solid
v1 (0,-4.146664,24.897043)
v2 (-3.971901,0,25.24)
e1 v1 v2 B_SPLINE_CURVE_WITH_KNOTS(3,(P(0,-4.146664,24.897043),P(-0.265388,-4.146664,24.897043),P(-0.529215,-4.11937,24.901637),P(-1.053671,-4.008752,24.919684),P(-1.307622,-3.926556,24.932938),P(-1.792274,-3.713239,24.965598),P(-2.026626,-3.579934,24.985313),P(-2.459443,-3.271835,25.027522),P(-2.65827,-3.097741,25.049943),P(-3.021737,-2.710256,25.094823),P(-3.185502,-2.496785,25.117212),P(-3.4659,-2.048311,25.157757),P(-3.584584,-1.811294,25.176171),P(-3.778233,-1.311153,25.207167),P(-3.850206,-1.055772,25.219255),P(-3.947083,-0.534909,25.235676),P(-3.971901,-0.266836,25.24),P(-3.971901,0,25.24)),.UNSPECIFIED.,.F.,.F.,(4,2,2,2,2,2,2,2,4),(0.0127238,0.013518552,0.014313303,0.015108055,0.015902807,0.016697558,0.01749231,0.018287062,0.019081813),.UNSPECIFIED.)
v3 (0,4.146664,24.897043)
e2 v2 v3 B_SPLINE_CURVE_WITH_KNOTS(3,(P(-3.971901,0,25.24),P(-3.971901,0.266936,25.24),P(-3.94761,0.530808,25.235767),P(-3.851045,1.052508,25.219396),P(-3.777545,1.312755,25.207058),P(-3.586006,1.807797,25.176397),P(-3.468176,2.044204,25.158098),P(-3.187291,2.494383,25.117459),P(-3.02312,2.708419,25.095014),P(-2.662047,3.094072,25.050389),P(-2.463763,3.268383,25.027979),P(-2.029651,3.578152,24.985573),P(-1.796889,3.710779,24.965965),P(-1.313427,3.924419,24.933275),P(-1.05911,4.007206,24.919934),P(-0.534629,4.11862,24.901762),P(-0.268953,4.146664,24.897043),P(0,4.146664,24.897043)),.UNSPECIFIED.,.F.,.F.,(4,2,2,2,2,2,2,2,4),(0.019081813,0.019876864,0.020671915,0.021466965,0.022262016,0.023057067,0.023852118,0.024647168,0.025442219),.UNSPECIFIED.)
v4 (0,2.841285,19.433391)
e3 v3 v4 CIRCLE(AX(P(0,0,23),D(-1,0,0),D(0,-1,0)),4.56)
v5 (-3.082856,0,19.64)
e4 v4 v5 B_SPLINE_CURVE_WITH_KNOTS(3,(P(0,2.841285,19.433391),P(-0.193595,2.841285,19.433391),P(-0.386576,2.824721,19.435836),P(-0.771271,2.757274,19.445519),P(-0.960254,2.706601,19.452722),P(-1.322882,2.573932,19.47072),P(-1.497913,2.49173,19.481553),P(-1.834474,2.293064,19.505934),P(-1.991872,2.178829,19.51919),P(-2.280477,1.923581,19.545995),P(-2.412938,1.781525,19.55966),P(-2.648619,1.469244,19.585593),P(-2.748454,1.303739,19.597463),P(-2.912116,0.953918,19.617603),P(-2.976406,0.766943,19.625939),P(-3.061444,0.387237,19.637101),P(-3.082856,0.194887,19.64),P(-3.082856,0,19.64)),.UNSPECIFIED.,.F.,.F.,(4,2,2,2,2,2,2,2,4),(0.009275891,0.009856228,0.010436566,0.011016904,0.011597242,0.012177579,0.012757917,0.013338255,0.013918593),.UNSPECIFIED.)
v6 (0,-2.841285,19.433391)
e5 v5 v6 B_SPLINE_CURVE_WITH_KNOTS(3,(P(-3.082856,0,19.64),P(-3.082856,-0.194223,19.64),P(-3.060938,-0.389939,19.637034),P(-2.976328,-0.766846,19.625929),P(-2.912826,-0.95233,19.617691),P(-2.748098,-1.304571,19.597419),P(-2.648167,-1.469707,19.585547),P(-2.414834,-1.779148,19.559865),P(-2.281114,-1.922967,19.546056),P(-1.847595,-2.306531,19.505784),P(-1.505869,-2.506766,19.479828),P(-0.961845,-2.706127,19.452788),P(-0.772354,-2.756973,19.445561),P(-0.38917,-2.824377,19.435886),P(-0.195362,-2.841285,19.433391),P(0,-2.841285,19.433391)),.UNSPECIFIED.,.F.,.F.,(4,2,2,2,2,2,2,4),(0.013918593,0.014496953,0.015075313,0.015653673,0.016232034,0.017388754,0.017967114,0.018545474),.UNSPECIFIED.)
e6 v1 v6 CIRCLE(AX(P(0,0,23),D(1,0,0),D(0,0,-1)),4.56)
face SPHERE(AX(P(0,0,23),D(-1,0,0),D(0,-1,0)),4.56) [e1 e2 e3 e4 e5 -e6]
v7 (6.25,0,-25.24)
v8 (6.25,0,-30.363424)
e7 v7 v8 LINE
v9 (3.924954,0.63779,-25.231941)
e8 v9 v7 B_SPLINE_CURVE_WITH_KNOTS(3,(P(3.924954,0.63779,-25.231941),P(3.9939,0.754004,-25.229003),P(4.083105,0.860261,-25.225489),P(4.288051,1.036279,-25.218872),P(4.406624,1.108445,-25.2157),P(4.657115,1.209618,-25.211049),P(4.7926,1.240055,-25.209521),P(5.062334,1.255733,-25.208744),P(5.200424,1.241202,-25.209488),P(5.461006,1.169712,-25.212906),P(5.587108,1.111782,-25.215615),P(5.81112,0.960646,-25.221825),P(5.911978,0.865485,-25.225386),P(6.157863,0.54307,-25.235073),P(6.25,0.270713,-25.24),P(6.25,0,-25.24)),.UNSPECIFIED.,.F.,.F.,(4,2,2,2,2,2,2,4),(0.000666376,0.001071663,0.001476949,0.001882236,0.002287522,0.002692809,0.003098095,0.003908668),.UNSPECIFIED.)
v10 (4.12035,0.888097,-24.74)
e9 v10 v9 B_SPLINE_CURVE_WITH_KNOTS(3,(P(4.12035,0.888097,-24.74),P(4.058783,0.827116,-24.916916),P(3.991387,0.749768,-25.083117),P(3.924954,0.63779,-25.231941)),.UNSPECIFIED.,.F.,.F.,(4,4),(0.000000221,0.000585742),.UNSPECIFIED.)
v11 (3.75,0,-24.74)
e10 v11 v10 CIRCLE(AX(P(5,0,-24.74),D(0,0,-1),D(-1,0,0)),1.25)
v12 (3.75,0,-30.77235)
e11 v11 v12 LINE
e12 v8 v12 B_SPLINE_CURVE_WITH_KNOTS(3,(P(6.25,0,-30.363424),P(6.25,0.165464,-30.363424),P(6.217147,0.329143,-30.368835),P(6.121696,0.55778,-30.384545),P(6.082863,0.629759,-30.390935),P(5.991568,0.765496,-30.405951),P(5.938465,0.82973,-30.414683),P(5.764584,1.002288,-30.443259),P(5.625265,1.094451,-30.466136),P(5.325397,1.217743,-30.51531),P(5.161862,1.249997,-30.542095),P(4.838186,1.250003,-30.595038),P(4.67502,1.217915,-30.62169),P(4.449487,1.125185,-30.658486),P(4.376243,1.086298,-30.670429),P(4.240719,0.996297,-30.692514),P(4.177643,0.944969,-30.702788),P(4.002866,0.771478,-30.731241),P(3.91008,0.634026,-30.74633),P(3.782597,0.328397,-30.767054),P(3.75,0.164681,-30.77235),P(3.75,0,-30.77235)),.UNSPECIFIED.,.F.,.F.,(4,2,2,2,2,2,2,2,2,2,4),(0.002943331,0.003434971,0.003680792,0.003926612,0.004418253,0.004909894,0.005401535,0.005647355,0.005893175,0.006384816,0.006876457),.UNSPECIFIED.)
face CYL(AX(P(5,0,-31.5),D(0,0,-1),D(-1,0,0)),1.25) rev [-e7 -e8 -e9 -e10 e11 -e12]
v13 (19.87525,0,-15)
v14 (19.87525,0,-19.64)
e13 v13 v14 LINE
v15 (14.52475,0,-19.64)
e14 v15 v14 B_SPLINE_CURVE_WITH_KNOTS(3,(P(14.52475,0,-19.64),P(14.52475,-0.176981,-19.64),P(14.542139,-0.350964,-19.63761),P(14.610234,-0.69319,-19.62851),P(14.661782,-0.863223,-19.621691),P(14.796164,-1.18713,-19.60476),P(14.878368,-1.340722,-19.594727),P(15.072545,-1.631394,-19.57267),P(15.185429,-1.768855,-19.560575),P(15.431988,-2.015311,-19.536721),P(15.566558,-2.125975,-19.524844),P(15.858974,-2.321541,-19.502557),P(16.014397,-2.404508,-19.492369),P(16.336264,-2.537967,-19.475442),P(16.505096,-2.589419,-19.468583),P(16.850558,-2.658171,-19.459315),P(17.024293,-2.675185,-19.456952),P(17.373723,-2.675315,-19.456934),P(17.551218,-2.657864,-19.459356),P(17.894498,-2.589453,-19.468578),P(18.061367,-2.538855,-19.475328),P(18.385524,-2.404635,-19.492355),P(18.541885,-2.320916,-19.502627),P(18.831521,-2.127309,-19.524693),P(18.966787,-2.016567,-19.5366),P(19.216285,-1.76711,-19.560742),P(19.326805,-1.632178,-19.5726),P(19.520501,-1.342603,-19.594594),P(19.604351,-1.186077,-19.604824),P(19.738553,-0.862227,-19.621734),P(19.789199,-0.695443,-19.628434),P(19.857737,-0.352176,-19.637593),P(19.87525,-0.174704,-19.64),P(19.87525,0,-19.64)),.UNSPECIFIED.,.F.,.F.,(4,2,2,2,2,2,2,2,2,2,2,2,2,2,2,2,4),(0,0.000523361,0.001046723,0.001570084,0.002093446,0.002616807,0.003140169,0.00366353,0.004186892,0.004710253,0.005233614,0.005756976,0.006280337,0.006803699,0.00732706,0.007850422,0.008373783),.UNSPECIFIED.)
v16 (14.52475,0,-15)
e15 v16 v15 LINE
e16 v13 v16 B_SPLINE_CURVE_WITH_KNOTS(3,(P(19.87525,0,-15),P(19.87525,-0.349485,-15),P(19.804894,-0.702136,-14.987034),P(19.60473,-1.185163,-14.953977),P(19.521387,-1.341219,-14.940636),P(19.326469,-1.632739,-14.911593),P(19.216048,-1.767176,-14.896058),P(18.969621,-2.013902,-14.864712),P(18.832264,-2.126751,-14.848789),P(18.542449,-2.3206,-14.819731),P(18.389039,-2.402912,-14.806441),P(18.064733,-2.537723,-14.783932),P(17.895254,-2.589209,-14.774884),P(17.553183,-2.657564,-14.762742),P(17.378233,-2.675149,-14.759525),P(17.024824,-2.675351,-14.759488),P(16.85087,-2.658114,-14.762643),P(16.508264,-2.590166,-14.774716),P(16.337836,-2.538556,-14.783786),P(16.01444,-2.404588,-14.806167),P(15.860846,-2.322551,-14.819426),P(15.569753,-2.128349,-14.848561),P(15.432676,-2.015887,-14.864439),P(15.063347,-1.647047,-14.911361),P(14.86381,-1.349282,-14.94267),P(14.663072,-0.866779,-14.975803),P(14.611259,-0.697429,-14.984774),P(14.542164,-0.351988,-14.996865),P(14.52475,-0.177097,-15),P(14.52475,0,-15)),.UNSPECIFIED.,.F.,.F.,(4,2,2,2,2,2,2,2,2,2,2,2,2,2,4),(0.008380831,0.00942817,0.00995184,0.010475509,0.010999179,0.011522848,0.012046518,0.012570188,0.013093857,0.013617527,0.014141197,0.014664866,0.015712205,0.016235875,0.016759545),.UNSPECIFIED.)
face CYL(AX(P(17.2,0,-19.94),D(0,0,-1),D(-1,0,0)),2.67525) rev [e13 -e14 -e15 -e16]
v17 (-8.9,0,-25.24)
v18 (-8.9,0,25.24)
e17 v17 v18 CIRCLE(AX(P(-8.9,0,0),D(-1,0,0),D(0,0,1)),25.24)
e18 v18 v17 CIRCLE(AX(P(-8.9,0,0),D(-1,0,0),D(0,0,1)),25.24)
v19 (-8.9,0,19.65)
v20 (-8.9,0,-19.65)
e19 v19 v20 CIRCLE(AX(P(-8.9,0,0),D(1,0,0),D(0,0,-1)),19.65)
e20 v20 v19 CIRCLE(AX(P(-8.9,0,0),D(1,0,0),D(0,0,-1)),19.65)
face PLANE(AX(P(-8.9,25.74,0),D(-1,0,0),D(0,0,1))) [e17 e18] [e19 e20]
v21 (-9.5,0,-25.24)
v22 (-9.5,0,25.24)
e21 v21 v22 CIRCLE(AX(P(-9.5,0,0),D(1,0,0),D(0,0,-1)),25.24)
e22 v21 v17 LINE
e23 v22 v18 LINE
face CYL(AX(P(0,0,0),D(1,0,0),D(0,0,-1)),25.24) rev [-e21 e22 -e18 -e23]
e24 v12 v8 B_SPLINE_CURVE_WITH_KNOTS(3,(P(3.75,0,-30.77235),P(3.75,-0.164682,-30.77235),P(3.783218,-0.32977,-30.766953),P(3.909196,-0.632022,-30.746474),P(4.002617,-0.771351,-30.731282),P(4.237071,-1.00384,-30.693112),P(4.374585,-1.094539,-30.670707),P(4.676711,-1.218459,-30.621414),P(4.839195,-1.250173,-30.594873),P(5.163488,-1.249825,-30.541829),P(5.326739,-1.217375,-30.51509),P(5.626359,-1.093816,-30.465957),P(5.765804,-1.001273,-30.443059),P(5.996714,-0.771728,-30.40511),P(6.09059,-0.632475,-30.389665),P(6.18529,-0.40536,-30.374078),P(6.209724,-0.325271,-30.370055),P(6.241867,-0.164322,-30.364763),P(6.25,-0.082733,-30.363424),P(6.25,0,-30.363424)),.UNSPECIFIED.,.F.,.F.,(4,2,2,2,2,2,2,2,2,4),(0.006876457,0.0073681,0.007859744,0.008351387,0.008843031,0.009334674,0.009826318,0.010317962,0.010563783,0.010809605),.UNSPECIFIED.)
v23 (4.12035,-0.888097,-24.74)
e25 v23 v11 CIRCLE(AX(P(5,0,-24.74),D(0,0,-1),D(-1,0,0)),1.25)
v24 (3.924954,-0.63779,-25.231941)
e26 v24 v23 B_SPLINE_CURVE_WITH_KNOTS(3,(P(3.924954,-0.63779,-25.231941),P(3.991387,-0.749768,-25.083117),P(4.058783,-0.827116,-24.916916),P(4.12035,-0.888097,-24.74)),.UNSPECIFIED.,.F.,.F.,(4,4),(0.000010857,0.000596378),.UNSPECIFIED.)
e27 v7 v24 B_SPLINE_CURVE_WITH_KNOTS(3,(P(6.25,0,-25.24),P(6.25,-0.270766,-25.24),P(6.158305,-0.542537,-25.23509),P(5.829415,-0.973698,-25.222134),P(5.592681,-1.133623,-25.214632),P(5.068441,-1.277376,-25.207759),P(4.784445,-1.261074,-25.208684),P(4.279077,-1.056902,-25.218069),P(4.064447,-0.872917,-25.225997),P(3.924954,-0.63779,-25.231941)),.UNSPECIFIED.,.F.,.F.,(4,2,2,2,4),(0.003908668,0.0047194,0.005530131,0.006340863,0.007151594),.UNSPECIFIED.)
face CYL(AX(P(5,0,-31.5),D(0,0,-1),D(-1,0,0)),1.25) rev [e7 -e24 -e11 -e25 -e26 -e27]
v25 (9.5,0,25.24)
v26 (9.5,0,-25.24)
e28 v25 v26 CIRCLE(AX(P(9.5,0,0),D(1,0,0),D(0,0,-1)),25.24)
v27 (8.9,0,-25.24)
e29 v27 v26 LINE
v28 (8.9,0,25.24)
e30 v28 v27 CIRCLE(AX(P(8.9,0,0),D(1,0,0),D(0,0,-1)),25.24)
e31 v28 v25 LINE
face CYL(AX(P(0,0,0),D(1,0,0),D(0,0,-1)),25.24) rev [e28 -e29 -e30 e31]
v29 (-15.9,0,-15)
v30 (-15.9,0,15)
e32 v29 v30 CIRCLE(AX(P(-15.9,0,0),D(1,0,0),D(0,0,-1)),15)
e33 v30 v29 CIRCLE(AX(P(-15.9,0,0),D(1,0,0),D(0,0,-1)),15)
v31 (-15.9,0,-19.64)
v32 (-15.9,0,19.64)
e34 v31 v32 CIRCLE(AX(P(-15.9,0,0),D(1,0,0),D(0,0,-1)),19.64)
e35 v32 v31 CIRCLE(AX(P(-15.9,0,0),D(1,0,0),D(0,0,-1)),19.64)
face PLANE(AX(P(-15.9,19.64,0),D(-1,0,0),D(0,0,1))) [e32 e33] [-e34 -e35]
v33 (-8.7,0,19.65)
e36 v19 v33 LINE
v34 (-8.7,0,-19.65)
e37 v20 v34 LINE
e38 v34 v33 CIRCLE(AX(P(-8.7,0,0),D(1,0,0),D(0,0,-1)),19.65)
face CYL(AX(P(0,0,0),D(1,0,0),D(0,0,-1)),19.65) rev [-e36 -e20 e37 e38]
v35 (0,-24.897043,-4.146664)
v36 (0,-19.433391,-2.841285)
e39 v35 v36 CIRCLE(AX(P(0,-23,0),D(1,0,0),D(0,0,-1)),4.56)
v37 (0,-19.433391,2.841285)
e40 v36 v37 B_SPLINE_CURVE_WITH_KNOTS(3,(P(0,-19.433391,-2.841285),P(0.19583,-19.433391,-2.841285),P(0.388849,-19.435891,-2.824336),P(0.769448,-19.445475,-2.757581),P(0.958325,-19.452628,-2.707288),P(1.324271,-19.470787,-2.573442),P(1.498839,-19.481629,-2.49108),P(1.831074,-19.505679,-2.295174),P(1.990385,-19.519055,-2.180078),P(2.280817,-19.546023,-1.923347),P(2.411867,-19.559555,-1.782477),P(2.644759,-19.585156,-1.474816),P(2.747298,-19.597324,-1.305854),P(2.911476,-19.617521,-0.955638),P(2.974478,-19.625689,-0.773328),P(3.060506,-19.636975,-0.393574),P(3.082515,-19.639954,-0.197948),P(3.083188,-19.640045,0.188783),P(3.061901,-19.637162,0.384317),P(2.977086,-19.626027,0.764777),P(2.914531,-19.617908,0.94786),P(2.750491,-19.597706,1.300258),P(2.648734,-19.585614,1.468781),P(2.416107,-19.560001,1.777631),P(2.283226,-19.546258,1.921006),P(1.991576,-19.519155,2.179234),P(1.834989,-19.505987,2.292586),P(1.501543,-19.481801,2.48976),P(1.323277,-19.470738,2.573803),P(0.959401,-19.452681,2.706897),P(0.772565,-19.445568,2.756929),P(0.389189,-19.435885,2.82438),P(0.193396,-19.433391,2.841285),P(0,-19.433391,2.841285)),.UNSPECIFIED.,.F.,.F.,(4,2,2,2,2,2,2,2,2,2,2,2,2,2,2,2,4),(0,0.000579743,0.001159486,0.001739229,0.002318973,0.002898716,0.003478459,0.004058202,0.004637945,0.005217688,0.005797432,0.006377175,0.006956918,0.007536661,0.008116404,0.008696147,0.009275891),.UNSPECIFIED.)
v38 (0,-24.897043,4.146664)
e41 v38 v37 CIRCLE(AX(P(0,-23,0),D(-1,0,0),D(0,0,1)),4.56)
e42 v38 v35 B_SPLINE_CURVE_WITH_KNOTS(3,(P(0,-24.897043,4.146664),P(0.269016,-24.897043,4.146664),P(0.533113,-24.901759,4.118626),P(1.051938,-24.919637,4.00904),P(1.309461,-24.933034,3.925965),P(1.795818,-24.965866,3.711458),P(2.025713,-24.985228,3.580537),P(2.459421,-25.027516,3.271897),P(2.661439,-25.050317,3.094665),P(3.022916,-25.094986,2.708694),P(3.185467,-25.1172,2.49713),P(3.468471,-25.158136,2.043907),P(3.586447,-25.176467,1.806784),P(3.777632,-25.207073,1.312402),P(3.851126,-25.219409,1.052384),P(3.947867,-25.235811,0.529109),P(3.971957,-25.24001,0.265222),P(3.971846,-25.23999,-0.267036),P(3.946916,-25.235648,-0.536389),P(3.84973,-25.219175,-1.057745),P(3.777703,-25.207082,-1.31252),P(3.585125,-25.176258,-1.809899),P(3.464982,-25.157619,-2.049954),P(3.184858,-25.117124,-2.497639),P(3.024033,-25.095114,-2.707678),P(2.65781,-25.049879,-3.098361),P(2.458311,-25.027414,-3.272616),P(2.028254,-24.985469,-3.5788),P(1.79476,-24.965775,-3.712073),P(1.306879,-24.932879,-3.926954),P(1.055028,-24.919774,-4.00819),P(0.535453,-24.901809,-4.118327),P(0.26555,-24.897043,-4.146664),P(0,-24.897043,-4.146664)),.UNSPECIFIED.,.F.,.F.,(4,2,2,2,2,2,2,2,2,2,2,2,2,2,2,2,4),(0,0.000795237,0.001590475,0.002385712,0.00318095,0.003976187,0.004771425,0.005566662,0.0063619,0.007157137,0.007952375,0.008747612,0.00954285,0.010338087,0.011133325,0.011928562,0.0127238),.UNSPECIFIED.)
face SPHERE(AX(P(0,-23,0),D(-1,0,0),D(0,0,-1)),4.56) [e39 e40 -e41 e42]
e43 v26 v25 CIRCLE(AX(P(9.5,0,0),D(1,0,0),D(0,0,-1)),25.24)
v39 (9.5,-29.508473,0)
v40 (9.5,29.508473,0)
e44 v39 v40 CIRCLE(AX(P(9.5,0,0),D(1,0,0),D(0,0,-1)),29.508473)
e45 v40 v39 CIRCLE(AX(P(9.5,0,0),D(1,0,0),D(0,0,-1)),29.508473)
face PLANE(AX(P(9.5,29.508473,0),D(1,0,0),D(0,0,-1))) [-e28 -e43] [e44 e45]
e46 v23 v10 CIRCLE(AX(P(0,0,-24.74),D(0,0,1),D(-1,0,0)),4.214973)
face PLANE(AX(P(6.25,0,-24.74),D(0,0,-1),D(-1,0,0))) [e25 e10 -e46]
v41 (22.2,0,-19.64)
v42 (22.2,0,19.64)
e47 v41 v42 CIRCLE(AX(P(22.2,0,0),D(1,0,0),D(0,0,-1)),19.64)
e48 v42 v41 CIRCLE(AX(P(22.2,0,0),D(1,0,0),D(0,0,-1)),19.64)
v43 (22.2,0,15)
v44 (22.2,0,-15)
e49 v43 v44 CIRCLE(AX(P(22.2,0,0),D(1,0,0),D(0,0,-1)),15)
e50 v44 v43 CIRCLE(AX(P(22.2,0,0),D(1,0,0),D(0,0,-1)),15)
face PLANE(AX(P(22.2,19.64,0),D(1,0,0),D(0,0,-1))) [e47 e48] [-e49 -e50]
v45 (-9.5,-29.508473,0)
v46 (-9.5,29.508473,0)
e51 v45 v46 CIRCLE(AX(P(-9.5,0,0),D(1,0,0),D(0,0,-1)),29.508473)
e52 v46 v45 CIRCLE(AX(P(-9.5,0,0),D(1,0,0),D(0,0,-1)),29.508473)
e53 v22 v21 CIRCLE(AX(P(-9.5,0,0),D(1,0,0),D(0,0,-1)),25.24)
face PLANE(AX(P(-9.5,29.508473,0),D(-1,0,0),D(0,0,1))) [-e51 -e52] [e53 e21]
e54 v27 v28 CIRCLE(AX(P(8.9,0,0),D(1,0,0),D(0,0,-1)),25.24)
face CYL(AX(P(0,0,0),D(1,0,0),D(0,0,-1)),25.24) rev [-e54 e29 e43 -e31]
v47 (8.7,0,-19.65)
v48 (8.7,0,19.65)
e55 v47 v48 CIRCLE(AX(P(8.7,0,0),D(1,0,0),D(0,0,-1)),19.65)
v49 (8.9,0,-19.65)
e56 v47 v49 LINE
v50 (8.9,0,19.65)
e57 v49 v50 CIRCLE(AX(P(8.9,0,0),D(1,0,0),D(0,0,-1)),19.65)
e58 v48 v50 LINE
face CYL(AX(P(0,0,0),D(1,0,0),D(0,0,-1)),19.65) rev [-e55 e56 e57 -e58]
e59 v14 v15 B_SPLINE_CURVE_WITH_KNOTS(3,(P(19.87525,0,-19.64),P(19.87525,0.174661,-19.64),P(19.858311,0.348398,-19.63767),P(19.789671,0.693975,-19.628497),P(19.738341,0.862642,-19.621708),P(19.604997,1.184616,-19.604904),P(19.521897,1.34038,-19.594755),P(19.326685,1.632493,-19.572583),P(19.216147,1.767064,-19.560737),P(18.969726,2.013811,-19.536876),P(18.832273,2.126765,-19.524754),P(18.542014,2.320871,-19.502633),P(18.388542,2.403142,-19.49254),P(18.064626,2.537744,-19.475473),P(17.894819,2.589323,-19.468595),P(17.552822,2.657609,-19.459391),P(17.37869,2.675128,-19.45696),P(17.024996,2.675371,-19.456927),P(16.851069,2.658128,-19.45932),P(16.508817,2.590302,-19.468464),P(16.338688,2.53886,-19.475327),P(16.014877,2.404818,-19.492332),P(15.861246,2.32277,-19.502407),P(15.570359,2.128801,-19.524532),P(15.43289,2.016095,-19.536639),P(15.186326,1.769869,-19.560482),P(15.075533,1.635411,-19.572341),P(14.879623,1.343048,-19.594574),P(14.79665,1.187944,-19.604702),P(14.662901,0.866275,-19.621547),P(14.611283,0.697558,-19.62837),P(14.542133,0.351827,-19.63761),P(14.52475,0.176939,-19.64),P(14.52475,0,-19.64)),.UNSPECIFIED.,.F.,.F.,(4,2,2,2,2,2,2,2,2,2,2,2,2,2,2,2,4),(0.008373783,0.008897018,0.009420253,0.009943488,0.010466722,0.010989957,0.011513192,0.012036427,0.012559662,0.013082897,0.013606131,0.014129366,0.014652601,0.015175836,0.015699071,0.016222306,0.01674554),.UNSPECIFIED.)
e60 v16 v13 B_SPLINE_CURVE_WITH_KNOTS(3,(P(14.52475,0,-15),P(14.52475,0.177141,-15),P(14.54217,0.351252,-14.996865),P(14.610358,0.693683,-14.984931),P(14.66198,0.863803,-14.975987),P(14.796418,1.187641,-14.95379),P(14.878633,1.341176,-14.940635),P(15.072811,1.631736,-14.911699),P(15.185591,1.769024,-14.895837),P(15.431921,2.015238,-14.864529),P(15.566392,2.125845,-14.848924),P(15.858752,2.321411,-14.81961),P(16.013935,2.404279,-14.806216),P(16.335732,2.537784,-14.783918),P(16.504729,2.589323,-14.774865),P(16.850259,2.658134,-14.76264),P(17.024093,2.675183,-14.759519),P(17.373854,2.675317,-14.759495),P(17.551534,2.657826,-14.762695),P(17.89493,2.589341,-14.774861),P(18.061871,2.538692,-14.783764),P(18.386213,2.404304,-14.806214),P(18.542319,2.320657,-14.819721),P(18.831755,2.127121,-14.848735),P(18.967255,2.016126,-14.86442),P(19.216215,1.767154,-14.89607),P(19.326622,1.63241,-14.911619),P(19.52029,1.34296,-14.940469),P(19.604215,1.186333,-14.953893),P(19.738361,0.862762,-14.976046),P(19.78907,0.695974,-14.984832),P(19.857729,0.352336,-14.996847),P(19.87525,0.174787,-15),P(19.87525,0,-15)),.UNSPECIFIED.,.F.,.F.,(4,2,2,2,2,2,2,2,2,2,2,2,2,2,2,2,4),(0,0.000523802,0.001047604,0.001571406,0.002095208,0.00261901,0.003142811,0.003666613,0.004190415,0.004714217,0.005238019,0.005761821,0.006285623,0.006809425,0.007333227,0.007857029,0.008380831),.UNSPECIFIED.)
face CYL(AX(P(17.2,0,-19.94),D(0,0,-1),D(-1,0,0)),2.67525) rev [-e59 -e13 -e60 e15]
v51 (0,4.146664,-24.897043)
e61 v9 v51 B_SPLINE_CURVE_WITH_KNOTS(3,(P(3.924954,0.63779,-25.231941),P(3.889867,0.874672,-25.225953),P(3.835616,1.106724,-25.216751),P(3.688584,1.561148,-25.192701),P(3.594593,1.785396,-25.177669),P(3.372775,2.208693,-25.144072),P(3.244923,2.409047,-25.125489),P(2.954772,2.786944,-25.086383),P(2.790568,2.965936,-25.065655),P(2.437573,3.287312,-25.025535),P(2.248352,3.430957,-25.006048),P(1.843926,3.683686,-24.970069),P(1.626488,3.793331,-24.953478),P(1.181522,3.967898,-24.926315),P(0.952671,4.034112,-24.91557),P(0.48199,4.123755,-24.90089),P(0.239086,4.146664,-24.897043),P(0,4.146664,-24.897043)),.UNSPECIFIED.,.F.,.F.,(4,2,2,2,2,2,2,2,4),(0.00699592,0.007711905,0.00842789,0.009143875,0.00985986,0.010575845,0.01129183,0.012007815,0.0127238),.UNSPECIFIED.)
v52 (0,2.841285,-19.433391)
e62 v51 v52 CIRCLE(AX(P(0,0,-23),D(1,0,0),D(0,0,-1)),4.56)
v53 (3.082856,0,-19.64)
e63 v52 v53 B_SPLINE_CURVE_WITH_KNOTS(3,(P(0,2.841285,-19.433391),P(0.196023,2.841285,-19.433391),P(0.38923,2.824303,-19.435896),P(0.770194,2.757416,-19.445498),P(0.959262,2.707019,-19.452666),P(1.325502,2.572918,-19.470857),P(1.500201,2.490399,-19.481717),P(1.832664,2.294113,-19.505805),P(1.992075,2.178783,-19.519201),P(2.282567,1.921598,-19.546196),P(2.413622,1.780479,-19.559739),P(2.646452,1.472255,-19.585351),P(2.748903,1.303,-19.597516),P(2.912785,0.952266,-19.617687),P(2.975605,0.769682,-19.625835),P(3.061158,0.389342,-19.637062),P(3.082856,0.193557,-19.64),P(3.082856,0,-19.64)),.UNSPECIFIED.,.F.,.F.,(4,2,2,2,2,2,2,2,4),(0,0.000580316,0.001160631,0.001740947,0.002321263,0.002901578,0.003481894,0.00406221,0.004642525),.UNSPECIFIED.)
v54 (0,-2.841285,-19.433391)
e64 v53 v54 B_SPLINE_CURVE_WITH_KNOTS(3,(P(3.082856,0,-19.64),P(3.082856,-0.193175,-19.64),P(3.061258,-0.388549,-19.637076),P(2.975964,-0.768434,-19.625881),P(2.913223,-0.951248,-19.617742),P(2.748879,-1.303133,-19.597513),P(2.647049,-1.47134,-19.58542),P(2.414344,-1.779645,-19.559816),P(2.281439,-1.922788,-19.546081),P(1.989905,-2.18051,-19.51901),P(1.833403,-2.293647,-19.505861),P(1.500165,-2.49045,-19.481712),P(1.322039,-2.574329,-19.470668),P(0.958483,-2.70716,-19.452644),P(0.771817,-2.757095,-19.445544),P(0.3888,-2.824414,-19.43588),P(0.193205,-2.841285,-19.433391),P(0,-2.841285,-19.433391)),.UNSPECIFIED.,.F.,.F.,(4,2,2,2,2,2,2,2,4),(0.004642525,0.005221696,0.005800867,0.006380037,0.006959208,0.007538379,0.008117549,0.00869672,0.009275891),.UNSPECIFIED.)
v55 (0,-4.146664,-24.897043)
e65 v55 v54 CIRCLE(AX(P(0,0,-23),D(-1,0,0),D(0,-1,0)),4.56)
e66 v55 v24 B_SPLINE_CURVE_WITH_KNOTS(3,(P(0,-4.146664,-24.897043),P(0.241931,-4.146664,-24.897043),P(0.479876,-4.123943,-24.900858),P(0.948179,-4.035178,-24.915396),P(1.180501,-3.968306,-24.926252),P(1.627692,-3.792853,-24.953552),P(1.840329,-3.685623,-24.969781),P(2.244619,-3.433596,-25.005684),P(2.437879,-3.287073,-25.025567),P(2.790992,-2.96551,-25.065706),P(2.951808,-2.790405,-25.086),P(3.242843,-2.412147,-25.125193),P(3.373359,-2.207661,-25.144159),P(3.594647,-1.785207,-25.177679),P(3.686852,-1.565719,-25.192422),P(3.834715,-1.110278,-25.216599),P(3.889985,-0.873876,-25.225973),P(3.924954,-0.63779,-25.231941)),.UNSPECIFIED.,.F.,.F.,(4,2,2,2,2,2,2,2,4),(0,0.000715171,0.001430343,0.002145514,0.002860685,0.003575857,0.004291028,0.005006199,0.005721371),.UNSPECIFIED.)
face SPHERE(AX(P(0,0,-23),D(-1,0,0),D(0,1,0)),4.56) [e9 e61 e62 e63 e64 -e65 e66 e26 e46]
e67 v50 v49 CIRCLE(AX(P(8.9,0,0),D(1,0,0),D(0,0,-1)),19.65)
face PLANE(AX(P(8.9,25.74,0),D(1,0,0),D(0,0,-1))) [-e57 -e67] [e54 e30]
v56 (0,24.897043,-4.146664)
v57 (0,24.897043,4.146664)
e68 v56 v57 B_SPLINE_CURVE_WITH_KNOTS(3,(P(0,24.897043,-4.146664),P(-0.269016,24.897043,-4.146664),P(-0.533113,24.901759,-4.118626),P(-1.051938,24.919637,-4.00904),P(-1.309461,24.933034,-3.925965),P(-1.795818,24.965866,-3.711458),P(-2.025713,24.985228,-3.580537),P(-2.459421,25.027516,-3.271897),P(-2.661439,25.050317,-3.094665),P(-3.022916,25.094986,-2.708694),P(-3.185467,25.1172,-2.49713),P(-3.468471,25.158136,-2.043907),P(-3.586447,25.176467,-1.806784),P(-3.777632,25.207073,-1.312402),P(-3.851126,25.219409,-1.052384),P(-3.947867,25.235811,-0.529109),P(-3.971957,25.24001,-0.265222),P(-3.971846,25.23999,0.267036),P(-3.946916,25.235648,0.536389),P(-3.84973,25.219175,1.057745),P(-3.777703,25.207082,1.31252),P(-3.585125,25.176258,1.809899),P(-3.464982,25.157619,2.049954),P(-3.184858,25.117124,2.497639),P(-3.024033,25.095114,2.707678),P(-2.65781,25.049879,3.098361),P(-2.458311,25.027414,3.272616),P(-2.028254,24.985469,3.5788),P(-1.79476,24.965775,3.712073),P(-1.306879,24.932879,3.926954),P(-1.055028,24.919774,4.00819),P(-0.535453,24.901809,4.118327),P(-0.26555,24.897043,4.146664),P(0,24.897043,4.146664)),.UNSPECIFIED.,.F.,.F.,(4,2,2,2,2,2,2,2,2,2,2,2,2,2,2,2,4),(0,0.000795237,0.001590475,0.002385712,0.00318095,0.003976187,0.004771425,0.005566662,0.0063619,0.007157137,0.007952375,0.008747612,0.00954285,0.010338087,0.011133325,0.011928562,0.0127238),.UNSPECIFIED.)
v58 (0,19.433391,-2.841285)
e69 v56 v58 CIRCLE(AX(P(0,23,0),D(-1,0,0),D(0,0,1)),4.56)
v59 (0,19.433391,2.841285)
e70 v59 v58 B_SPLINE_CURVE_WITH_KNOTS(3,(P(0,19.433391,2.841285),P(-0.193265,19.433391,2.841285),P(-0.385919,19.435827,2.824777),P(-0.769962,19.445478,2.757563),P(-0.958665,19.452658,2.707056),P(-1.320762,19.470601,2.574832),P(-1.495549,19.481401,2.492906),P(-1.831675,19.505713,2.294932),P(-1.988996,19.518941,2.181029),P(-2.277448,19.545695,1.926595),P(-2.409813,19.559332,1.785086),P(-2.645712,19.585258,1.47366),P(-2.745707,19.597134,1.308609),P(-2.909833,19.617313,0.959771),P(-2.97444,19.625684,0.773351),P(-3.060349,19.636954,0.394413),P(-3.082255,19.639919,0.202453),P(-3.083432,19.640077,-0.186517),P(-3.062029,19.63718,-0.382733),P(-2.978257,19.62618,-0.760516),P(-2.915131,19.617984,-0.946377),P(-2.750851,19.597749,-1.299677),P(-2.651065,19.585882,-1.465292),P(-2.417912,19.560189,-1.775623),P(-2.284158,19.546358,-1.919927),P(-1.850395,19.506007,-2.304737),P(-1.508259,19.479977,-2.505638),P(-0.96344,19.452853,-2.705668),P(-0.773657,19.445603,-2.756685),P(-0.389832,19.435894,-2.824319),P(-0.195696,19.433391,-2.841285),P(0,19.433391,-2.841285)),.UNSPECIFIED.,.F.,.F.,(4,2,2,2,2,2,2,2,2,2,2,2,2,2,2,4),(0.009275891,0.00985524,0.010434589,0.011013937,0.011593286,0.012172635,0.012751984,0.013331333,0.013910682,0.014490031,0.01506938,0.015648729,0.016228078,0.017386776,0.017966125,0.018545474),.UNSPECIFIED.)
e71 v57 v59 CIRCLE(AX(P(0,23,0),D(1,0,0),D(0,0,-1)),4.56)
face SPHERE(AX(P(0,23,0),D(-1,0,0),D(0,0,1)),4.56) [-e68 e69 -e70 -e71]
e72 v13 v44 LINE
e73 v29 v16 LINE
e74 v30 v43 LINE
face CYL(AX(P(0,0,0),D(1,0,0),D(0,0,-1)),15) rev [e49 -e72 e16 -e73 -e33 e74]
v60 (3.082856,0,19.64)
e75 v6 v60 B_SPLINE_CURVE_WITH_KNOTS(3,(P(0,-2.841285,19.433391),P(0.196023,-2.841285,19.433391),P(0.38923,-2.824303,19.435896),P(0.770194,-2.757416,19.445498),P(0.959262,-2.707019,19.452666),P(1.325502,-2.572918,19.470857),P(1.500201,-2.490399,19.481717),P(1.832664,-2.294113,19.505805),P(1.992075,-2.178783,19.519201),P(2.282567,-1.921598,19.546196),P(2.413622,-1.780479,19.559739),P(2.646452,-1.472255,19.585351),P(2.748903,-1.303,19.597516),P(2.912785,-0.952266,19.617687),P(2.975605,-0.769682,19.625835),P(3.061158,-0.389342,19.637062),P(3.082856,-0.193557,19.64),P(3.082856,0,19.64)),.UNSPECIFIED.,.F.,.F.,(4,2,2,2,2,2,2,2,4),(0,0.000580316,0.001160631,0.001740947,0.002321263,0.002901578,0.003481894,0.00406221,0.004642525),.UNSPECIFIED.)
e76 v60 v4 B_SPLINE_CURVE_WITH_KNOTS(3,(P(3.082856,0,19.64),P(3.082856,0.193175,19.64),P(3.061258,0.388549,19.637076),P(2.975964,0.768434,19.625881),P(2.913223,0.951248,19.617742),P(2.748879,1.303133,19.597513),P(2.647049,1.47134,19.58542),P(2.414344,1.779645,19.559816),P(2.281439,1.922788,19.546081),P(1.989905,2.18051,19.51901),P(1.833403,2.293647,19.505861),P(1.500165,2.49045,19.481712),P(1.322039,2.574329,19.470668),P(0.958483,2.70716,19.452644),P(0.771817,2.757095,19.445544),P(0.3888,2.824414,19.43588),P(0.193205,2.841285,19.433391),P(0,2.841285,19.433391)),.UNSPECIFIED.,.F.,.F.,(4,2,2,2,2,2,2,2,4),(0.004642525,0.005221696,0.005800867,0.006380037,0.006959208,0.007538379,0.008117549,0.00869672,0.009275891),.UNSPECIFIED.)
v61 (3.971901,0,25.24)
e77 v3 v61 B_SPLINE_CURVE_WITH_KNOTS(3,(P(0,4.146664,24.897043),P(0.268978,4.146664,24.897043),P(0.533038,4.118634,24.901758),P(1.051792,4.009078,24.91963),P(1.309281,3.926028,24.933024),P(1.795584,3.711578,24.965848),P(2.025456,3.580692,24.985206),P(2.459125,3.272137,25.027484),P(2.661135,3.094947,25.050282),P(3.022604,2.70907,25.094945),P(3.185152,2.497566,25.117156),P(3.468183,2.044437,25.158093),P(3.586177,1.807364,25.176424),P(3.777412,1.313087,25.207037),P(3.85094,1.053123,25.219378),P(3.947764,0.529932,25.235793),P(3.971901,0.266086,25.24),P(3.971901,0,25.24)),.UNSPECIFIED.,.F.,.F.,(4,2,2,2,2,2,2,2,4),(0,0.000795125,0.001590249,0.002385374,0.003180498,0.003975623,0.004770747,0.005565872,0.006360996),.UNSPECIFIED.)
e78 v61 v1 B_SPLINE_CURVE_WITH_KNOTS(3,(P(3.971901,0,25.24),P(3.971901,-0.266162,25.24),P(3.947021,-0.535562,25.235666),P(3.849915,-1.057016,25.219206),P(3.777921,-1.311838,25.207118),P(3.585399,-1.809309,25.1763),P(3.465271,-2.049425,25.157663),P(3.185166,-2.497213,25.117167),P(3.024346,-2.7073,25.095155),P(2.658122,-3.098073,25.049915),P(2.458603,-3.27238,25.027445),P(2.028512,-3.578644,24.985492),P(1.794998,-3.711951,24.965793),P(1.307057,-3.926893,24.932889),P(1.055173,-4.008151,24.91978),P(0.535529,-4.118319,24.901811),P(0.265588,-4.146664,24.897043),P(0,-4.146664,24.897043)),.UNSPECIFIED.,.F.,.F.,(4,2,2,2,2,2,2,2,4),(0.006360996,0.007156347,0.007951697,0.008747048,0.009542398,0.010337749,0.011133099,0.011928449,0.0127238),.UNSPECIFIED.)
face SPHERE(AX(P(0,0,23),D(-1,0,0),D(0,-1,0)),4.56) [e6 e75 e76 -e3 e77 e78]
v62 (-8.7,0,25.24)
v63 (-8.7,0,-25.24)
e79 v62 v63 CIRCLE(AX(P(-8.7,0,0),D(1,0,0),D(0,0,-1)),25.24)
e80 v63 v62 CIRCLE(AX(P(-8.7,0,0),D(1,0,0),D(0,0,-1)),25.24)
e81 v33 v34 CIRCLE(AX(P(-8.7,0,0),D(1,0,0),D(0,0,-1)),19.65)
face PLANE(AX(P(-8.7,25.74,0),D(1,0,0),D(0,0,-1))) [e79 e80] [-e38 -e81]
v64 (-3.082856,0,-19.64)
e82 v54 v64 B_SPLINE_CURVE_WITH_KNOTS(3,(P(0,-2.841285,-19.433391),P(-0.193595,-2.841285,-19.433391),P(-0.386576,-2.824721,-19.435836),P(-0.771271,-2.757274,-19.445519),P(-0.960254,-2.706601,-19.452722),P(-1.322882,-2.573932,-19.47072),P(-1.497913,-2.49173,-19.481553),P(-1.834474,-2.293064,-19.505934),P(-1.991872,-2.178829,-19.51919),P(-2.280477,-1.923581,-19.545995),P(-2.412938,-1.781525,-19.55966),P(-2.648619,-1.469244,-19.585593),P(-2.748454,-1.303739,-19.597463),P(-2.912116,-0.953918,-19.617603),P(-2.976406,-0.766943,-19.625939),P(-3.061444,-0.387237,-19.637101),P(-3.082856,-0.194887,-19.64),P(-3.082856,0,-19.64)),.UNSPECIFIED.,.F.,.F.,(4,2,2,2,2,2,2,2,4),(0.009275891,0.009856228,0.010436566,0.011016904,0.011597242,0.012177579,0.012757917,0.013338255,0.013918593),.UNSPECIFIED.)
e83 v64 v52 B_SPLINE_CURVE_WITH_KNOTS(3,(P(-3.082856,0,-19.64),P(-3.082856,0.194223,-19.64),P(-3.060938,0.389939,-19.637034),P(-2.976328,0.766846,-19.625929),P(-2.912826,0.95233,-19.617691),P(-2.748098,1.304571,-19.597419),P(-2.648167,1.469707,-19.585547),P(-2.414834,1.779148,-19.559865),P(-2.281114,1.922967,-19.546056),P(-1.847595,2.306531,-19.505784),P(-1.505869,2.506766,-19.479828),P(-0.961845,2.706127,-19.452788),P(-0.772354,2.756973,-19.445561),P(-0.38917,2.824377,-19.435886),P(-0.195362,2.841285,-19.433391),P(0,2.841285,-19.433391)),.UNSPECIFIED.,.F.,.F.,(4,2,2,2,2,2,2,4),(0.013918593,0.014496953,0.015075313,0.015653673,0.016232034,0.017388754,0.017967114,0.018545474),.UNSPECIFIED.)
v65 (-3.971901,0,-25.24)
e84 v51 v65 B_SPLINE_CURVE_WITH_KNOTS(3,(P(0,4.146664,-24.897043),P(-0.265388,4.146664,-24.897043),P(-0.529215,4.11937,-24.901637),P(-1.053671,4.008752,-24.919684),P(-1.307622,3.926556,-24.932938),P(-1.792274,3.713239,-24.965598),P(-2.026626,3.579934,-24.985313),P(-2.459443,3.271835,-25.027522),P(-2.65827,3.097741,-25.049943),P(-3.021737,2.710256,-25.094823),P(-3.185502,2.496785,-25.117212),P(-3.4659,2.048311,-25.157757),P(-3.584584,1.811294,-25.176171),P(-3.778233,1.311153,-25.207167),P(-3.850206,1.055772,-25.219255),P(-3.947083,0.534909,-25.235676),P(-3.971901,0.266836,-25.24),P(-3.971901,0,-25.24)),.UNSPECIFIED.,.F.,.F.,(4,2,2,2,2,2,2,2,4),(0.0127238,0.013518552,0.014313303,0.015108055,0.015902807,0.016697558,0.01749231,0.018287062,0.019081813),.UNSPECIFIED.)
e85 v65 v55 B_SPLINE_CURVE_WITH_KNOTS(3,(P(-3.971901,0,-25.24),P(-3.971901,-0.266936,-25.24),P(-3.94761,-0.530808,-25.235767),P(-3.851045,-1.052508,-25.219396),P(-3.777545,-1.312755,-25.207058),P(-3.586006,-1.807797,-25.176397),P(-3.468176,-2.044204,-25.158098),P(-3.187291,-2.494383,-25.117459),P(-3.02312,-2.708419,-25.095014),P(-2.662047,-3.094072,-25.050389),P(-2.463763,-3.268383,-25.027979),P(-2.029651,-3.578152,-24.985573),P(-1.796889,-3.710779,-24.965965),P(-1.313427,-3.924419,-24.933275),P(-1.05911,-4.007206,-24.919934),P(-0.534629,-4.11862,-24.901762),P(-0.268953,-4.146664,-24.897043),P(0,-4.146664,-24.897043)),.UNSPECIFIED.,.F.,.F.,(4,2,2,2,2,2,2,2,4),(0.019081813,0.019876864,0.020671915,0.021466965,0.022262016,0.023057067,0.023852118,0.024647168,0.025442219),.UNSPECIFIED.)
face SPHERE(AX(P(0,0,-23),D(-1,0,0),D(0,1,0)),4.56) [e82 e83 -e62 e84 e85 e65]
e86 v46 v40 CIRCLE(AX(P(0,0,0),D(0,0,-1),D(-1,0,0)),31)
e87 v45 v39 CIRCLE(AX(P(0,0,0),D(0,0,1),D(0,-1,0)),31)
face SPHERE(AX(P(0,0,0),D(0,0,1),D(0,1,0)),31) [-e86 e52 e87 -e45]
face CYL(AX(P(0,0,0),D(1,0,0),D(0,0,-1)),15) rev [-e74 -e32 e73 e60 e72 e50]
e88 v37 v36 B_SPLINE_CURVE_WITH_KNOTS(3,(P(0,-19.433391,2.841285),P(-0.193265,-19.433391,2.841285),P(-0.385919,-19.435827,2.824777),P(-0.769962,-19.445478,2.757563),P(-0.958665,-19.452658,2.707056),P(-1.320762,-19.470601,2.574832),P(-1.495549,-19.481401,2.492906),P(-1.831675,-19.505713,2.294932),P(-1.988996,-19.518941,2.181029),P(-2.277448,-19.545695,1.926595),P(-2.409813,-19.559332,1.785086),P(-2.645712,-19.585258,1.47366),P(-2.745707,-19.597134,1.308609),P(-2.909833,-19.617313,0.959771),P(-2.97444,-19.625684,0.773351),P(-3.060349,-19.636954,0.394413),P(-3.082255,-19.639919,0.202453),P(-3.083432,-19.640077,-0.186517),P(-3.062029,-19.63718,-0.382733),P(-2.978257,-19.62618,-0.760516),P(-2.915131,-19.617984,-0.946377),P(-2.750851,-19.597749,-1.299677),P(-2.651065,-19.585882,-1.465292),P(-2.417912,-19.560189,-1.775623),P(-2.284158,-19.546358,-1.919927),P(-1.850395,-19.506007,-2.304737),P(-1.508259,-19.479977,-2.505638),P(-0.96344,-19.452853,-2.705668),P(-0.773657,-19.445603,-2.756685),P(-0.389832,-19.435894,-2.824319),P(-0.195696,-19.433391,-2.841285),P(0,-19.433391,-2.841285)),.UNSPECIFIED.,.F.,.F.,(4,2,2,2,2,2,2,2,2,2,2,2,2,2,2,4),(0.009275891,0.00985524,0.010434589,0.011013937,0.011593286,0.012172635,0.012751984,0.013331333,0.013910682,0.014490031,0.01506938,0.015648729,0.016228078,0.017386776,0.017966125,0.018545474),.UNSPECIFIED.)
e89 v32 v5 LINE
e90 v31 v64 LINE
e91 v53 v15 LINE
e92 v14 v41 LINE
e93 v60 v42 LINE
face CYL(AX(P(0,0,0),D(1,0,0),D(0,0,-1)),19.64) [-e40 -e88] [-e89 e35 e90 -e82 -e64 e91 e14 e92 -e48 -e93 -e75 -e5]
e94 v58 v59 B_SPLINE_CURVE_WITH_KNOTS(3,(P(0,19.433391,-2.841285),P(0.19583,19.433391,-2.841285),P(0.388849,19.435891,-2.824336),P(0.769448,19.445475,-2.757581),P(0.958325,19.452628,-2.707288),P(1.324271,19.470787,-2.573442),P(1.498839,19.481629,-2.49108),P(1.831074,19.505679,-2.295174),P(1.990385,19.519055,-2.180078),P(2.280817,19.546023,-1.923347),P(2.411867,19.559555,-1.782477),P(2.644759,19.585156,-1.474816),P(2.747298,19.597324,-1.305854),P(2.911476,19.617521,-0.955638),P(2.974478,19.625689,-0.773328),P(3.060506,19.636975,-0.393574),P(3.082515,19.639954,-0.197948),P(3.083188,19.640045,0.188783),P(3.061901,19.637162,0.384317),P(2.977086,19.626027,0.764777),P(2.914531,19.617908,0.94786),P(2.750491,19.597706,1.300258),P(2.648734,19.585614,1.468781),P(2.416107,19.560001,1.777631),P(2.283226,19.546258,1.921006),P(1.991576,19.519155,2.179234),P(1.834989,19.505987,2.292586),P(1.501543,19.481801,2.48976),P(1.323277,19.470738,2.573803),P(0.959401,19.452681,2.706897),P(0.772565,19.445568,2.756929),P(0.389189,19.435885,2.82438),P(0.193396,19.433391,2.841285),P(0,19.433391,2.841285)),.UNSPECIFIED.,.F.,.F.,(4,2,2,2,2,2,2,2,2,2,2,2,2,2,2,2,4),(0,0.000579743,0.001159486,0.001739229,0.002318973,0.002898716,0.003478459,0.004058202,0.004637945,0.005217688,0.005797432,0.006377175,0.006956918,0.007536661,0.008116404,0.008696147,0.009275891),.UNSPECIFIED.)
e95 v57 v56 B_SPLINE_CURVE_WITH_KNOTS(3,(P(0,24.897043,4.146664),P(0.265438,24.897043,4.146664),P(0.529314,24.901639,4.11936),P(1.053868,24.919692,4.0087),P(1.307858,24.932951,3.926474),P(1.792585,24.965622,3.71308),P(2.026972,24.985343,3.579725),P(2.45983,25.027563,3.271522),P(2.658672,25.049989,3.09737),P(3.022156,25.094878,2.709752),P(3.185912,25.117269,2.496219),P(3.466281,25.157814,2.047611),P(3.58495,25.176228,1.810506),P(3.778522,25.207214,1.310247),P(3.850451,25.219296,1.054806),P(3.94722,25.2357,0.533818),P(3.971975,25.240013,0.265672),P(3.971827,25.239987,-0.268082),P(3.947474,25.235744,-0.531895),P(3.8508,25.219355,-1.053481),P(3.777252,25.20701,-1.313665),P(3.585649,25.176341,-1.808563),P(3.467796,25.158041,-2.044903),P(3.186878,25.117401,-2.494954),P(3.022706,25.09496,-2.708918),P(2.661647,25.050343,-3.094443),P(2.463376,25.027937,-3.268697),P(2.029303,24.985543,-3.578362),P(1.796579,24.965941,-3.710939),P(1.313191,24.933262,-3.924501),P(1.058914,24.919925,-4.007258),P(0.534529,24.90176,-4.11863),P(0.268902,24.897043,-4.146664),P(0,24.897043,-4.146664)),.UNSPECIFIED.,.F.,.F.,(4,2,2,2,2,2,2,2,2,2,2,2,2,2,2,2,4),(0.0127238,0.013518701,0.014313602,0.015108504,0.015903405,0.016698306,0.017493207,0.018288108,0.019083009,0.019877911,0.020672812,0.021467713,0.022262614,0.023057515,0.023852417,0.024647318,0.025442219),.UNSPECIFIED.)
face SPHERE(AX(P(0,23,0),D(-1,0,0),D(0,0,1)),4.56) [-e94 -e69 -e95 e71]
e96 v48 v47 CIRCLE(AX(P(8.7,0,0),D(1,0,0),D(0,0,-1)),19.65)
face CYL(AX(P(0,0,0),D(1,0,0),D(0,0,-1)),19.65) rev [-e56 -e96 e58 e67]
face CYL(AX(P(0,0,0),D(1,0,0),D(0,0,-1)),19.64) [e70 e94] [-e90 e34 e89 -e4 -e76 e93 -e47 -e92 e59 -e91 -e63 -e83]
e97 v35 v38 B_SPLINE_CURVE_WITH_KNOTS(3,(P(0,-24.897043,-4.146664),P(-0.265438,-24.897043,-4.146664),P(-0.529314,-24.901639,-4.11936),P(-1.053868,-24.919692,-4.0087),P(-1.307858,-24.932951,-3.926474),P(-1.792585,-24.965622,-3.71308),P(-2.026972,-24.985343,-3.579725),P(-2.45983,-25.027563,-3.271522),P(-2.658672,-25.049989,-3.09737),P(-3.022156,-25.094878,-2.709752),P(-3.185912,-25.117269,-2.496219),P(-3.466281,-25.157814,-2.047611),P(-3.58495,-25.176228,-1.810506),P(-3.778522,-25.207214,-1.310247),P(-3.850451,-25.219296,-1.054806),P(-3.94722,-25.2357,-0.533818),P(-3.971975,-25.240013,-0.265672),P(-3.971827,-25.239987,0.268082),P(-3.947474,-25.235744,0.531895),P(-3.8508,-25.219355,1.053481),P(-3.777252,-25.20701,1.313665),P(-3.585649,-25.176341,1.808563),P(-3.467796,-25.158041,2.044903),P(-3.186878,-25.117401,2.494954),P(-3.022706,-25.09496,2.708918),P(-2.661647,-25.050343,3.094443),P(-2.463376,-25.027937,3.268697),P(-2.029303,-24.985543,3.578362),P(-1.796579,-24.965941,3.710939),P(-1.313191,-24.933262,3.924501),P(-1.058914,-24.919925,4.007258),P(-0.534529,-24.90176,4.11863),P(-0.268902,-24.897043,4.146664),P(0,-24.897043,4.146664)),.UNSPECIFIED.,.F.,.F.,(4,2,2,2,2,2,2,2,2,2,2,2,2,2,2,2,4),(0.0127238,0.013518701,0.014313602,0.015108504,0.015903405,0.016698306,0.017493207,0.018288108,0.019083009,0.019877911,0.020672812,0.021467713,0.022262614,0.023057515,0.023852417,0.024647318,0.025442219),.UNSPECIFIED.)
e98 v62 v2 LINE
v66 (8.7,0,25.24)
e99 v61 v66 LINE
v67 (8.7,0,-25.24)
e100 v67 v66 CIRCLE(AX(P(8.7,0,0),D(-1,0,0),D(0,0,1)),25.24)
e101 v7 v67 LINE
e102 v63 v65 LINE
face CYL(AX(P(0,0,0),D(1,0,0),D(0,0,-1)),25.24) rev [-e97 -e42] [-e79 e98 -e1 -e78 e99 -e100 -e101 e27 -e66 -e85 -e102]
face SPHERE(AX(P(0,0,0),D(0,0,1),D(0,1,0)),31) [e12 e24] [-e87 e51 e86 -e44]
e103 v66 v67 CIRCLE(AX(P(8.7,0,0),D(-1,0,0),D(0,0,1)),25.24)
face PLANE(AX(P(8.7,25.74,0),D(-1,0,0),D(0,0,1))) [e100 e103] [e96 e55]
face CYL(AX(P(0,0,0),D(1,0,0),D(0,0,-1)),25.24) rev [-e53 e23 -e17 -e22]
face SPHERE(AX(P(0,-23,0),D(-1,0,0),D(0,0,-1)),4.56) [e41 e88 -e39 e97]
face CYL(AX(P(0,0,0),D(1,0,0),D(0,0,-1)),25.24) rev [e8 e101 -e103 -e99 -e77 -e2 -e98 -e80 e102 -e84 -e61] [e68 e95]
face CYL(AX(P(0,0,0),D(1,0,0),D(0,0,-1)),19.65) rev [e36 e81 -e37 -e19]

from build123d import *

# Parameters (mm, degrees)
SKETCH_2_W               = 38.1
SKETCH_2_H               = 4.64
PATTERN_CIRCULAR_1_COUNT = 4
SKETCH_5_W               = 0.2
SKETCH_5_H               = 6.09
SKETCH_4_W               = 2.67525
SKETCH_4_H               = 6.94
SKETCH_6_W               = 1.25
SKETCH_6_H               = 6.76


with BuildPart() as part:
    # 草图3 → Revolve 502 (revolve)
    with BuildSketch(Plane(origin=(0, 0, 0), x_dir=(0, 0, -1), z_dir=(1, 0, 0))):
        with BuildLine():
            Line((0, 18.44), (0, 27.56))
            ThreePointArc((0, 27.56), (4.56, 23), (0, 18.44))
        make_face()
    revolve_502 = revolve(axis=Axis((0, 0, 0), (0, 1, 0)))

    # 草图2 → 凸台-旋转3 (revolve)
    with BuildSketch(Plane.XY, mode=Mode.PRIVATE) as revolve_3_sk:
        with BuildLine():
            Line((-9.5, 25.24), (9.5, 25.24))
            Line((9.5, 25.24), (9.5, 29.508473359))
            ThreePointArc((9.5, 29.508473359), (0, 31), (-9.5, 29.508473359))
            Line((-9.5, 29.508473359), (-9.5, 25.24))
        make_face()
        with Locations((3.15, 17.32)):
            Rectangle(SKETCH_2_W, SKETCH_2_H)
    revolve(revolve_3_sk.sketch.rotate(Axis((0, 0, 0), (-1, 0, 0)), 90), axis=Axis((0, 0, 0), (-1, 0, 0)))

    # 阵列(圆周)1: Revolve 502 ×4 about axis
    pattern_circular_1_axis = Axis((0, 0, 0), (1, 0, 0))
    for i in range(1, PATTERN_CIRCULAR_1_COUNT):
        add(revolve_502.rotate(pattern_circular_1_axis, i * 360 / PATTERN_CIRCULAR_1_COUNT))

    # 草图5 → 凸台-旋转4 (revolve)
    with BuildSketch(Plane.XY, mode=Mode.PRIVATE) as revolve_4_sk:
        with Locations((-8.8, 22.695)):
            Rectangle(SKETCH_5_W, SKETCH_5_H)
        with Locations((8.8, 22.695)):
            Rectangle(SKETCH_5_W, SKETCH_5_H)
    revolve(revolve_4_sk.sketch.rotate(Axis((0, 0, 0), (-1, 0, 0)), 90), axis=Axis((0, 0, 0), (-1, 0, 0)))

    # 草图4 → 切除-旋转1 (revolve, cut)
    with BuildSketch(Plane(origin=(0, 0, 0), x_dir=(1, 0, 0), z_dir=(0, 1, 0)), mode=Mode.PRIVATE) as cut_revolve_1_sk:
        with Locations((18.537625, 16.47)):
            Rectangle(SKETCH_4_W, SKETCH_4_H)
    revolve(cut_revolve_1_sk.sketch.rotate(Axis((17.2, 0, -19.94), (0, 0, 1)), 180), axis=Axis((17.2, 0, -19.94), (0, 0, 1)), mode=Mode.SUBTRACT)

    # 草图6 → 切除-旋转2 (revolve, cut)
    with BuildSketch(Plane(origin=(0, 0, 0), x_dir=(1, 0, 0), z_dir=(0, 1, 0)), mode=Mode.PRIVATE) as cut_revolve_2_sk:
        with Locations((5.625, 28.12)):
            Rectangle(SKETCH_6_W, SKETCH_6_H)
    revolve(cut_revolve_2_sk.sketch.rotate(Axis((5, 0, -31.5), (0, 0, 1)), 180), axis=Axis((5, 0, -31.5), (0, 0, 1)), mode=Mode.SUBTRACT)


solid = part.part
